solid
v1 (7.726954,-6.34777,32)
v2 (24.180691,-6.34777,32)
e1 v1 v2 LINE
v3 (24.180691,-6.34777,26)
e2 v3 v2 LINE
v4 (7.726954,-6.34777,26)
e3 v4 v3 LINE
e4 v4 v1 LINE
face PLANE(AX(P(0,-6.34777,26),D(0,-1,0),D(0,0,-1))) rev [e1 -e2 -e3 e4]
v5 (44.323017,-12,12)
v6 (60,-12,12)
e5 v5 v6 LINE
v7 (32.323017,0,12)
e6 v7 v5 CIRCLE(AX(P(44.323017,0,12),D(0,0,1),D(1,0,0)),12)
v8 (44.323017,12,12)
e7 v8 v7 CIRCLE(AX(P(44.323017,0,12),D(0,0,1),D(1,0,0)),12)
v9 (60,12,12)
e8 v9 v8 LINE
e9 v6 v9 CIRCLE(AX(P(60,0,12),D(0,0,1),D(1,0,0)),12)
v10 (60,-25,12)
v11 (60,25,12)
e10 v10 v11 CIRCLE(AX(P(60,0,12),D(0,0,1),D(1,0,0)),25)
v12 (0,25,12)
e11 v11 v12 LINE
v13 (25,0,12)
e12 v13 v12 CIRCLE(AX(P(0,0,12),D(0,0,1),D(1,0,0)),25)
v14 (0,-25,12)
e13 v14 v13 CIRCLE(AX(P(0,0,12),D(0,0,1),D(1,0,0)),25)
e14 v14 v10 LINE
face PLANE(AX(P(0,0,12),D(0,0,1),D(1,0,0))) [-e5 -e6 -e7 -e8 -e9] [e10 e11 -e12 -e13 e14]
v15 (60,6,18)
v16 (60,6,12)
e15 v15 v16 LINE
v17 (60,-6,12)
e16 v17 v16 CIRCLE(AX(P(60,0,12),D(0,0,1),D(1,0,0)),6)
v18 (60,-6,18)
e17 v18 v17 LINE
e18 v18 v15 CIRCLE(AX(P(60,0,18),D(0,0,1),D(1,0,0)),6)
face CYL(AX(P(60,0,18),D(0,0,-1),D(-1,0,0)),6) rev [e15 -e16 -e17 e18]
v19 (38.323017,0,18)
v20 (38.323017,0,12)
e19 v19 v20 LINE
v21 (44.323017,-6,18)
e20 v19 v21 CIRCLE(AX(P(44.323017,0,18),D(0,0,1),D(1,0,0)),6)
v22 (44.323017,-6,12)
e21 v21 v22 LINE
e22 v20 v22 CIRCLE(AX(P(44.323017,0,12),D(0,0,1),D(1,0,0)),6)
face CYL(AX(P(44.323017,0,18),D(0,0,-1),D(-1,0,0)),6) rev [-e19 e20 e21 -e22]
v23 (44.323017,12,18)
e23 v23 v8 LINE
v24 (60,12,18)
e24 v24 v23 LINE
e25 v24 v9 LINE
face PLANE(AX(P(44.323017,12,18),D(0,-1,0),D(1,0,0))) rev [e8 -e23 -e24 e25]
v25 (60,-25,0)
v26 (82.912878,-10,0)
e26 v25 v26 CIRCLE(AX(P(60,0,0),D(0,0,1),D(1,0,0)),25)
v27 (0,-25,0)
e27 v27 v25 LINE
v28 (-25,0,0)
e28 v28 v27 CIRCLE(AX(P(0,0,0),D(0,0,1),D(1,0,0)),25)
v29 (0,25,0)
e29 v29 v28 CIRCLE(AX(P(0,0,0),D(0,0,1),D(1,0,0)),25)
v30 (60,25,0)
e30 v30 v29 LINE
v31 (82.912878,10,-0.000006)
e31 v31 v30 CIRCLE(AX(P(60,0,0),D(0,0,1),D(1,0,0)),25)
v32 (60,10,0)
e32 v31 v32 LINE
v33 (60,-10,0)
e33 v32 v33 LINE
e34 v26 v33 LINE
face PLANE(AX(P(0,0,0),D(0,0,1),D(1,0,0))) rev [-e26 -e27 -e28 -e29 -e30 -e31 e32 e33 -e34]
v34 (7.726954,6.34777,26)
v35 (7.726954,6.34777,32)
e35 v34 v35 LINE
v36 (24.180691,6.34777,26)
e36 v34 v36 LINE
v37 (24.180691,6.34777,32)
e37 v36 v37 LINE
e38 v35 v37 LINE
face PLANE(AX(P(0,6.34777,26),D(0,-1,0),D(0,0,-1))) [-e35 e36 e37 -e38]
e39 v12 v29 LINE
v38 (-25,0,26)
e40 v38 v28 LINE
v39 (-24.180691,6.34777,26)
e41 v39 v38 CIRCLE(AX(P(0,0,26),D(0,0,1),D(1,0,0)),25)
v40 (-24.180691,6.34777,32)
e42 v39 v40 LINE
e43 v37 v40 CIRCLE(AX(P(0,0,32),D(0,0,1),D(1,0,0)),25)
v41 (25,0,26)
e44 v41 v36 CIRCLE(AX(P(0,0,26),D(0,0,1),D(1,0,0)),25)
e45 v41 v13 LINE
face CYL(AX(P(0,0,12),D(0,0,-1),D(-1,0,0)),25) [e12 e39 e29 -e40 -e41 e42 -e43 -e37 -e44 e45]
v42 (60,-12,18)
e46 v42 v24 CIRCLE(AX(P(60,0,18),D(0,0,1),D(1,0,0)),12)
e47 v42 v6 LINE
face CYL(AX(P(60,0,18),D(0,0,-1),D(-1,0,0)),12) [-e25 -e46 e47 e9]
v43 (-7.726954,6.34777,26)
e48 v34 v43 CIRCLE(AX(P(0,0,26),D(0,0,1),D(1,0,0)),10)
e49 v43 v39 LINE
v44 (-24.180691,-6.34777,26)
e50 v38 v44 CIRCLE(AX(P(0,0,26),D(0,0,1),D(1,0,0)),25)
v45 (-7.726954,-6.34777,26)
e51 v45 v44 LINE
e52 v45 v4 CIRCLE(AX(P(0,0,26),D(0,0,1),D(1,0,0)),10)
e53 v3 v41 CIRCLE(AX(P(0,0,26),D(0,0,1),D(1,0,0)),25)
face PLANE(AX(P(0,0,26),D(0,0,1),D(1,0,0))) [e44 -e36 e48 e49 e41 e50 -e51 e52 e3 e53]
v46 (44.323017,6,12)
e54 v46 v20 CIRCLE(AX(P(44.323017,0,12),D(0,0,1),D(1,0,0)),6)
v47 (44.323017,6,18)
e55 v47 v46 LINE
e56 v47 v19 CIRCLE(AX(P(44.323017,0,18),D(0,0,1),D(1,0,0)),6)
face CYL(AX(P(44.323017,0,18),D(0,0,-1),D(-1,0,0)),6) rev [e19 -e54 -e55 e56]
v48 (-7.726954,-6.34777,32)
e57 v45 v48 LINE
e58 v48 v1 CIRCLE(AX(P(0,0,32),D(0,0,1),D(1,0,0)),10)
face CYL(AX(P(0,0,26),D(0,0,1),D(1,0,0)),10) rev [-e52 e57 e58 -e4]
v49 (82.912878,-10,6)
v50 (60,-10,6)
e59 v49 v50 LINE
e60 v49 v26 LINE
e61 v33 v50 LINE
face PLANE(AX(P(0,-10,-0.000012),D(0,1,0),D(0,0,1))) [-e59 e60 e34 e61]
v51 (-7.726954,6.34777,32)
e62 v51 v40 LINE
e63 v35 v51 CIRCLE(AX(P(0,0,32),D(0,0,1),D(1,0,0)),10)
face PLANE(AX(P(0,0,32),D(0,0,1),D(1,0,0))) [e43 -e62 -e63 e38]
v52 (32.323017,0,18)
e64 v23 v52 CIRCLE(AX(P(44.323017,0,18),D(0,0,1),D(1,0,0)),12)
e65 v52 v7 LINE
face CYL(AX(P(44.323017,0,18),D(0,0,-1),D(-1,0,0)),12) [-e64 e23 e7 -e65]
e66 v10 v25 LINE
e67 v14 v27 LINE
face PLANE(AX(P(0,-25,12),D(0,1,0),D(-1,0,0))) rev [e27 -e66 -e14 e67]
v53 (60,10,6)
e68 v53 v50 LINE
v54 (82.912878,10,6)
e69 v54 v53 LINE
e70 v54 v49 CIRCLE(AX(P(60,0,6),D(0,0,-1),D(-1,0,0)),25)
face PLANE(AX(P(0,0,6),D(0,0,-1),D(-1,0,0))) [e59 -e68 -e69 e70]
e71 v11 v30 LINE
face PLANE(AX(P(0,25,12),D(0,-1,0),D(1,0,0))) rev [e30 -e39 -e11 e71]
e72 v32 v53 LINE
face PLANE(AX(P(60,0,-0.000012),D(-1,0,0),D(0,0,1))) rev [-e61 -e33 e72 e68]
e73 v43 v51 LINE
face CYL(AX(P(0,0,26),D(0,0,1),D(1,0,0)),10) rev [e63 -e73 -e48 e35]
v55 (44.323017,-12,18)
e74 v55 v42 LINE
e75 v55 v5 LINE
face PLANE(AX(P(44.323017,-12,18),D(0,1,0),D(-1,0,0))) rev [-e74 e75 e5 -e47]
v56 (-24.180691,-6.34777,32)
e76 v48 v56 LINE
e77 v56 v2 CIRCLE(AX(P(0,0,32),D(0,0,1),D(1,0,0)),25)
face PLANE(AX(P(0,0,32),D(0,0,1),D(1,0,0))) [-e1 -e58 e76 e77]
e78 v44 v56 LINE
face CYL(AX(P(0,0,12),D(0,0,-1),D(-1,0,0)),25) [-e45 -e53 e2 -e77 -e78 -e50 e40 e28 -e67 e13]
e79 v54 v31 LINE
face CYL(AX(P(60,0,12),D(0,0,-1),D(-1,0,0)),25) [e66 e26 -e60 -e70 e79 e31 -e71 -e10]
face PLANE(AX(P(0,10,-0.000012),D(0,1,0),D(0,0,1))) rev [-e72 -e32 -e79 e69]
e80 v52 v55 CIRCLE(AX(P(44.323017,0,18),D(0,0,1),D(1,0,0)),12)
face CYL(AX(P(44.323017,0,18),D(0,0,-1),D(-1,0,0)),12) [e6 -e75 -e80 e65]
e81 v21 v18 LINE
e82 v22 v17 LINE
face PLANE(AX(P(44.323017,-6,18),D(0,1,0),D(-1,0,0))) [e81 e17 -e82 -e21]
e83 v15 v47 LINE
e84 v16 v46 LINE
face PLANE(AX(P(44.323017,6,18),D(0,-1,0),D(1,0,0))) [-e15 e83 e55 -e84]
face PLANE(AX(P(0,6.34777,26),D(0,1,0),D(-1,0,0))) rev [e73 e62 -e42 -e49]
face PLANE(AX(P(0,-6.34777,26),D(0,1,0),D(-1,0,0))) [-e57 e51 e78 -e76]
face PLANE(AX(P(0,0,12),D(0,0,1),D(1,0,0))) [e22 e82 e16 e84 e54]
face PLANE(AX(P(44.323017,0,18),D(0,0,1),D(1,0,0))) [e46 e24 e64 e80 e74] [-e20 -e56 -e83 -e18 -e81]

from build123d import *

# Parameters (mm, degrees)
BASE_PLATE_DEPTH          = 12
HUB_BOSS_SKETCH_R         = 25
HUB_BOSS_DEPTH            = 20
HUB_START                 = -6
HUB_KEYHOLE_SLOT_SKETCH_R = 10
HUB_KEYHOLE_SLOT_DEPTH    = 6
SLOT_RIM_DEPTH            = 6
OBROUND_SLOT_DEPTH        = 95.201910809
OBROUND_SLOT_DEPTH_BACK   = 6


with BuildPart() as part:
    # Base Plate Sketch → Base Plate (new body)
    with BuildSketch(Plane.XY):
        with BuildLine():
            Line((0, 25), (60, 25))
            ThreePointArc((60, 25), (85, 0), (60, -25))
            Line((60, -25), (0, -25))
            ThreePointArc((0, -25), (-25, 0), (0, 25))
        make_face()
    extrude(amount=BASE_PLATE_DEPTH)

    # Hub Boss Sketch → Hub Boss (add)
    with BuildSketch(Plane.XY.offset(12)):
        with Locations(Location((0, 0, 0), (0, 0, 270))):
            Circle(HUB_BOSS_SKETCH_R)
    extrude(amount=HUB_BOSS_DEPTH)

    # Hub Keyhole Slot Sketch → Hub Keyhole Slot (cut)
    with BuildSketch(Plane.XY.offset(32).offset(HUB_START)):
        with BuildLine():
            ThreePointArc((-7.726954142, -6.347769662), (-10, 0), (-7.726954142, 6.347769662))
            Line((-7.726954142, 6.347769662), (-24.180691064, 6.347769662))
            ThreePointArc((-24.180691064, 6.347769662), (-25, 0), (-24.180691064, -6.347769662))
            Line((-24.180691064, -6.347769662), (-7.726954142, -6.347769662))
        make_face()
        Circle(HUB_KEYHOLE_SLOT_SKETCH_R)
        with BuildLine():
            Line((24.180691064, 6.347769662), (7.726954142, 6.347769662))
            ThreePointArc((7.726954142, 6.347769662), (9.414604119, 3.371235573), (10, 0))
            ThreePointArc((10, 0), (9.414604119, -3.371235573), (7.726954142, -6.347769662))
            Line((7.726954142, -6.347769662), (24.180691064, -6.347769662))
            ThreePointArc((24.180691064, -6.347769662), (24.794326736, -3.200212759), (25, 0))
            ThreePointArc((25, 0), (24.794326736, 3.200212759), (24.180691064, 6.347769662))
        make_face()
    extrude(amount=HUB_KEYHOLE_SLOT_DEPTH, mode=Mode.SUBTRACT)

    # Slot Rim Sketch → Slot Rim (add)
    with BuildSketch(Plane.XY.offset(12)):
        with BuildLine():
            Line((44.323016702, 12), (60, 12))
            ThreePointArc((60, 12), (72, 0), (60, -12))
            Line((60, -12), (44.323016702, -12))
            ThreePointArc((44.323016702, -12), (32.323016702, 0), (44.323016702, 12))
        make_face()
        with BuildLine():
            Line((44.323016702, 6), (60, 6))
            ThreePointArc((60, 6), (66, 0), (60, -6))
            Line((60, -6), (44.323016702, -6))
            ThreePointArc((44.323016702, -6), (38.323016702, 0), (44.323016702, 6))
        make_face(mode=Mode.SUBTRACT)
    extrude(amount=SLOT_RIM_DEPTH)

    # Obround Slot Sketch → Obround Slot (cut, two sides: drawn at the far end of the back side and taken through both)
    with BuildSketch(Plane(origin=(0, 0, 0), x_dir=(-1, 0, 0), z_dir=(0, 0, -1)).offset(-OBROUND_SLOT_DEPTH_BACK)):
        with BuildLine():
            ThreePointArc((-82.912878475, 10), (-85, 0), (-82.912878475, -10))
            Line((-82.912878475, -10), (-60, -10))
            Line((-60, -10), (-60, 10))
            Line((-60, 10), (-82.912878475, 10))
        make_face()
    extrude(amount=OBROUND_SLOT_DEPTH + OBROUND_SLOT_DEPTH_BACK, mode=Mode.SUBTRACT)


solid = part.part
